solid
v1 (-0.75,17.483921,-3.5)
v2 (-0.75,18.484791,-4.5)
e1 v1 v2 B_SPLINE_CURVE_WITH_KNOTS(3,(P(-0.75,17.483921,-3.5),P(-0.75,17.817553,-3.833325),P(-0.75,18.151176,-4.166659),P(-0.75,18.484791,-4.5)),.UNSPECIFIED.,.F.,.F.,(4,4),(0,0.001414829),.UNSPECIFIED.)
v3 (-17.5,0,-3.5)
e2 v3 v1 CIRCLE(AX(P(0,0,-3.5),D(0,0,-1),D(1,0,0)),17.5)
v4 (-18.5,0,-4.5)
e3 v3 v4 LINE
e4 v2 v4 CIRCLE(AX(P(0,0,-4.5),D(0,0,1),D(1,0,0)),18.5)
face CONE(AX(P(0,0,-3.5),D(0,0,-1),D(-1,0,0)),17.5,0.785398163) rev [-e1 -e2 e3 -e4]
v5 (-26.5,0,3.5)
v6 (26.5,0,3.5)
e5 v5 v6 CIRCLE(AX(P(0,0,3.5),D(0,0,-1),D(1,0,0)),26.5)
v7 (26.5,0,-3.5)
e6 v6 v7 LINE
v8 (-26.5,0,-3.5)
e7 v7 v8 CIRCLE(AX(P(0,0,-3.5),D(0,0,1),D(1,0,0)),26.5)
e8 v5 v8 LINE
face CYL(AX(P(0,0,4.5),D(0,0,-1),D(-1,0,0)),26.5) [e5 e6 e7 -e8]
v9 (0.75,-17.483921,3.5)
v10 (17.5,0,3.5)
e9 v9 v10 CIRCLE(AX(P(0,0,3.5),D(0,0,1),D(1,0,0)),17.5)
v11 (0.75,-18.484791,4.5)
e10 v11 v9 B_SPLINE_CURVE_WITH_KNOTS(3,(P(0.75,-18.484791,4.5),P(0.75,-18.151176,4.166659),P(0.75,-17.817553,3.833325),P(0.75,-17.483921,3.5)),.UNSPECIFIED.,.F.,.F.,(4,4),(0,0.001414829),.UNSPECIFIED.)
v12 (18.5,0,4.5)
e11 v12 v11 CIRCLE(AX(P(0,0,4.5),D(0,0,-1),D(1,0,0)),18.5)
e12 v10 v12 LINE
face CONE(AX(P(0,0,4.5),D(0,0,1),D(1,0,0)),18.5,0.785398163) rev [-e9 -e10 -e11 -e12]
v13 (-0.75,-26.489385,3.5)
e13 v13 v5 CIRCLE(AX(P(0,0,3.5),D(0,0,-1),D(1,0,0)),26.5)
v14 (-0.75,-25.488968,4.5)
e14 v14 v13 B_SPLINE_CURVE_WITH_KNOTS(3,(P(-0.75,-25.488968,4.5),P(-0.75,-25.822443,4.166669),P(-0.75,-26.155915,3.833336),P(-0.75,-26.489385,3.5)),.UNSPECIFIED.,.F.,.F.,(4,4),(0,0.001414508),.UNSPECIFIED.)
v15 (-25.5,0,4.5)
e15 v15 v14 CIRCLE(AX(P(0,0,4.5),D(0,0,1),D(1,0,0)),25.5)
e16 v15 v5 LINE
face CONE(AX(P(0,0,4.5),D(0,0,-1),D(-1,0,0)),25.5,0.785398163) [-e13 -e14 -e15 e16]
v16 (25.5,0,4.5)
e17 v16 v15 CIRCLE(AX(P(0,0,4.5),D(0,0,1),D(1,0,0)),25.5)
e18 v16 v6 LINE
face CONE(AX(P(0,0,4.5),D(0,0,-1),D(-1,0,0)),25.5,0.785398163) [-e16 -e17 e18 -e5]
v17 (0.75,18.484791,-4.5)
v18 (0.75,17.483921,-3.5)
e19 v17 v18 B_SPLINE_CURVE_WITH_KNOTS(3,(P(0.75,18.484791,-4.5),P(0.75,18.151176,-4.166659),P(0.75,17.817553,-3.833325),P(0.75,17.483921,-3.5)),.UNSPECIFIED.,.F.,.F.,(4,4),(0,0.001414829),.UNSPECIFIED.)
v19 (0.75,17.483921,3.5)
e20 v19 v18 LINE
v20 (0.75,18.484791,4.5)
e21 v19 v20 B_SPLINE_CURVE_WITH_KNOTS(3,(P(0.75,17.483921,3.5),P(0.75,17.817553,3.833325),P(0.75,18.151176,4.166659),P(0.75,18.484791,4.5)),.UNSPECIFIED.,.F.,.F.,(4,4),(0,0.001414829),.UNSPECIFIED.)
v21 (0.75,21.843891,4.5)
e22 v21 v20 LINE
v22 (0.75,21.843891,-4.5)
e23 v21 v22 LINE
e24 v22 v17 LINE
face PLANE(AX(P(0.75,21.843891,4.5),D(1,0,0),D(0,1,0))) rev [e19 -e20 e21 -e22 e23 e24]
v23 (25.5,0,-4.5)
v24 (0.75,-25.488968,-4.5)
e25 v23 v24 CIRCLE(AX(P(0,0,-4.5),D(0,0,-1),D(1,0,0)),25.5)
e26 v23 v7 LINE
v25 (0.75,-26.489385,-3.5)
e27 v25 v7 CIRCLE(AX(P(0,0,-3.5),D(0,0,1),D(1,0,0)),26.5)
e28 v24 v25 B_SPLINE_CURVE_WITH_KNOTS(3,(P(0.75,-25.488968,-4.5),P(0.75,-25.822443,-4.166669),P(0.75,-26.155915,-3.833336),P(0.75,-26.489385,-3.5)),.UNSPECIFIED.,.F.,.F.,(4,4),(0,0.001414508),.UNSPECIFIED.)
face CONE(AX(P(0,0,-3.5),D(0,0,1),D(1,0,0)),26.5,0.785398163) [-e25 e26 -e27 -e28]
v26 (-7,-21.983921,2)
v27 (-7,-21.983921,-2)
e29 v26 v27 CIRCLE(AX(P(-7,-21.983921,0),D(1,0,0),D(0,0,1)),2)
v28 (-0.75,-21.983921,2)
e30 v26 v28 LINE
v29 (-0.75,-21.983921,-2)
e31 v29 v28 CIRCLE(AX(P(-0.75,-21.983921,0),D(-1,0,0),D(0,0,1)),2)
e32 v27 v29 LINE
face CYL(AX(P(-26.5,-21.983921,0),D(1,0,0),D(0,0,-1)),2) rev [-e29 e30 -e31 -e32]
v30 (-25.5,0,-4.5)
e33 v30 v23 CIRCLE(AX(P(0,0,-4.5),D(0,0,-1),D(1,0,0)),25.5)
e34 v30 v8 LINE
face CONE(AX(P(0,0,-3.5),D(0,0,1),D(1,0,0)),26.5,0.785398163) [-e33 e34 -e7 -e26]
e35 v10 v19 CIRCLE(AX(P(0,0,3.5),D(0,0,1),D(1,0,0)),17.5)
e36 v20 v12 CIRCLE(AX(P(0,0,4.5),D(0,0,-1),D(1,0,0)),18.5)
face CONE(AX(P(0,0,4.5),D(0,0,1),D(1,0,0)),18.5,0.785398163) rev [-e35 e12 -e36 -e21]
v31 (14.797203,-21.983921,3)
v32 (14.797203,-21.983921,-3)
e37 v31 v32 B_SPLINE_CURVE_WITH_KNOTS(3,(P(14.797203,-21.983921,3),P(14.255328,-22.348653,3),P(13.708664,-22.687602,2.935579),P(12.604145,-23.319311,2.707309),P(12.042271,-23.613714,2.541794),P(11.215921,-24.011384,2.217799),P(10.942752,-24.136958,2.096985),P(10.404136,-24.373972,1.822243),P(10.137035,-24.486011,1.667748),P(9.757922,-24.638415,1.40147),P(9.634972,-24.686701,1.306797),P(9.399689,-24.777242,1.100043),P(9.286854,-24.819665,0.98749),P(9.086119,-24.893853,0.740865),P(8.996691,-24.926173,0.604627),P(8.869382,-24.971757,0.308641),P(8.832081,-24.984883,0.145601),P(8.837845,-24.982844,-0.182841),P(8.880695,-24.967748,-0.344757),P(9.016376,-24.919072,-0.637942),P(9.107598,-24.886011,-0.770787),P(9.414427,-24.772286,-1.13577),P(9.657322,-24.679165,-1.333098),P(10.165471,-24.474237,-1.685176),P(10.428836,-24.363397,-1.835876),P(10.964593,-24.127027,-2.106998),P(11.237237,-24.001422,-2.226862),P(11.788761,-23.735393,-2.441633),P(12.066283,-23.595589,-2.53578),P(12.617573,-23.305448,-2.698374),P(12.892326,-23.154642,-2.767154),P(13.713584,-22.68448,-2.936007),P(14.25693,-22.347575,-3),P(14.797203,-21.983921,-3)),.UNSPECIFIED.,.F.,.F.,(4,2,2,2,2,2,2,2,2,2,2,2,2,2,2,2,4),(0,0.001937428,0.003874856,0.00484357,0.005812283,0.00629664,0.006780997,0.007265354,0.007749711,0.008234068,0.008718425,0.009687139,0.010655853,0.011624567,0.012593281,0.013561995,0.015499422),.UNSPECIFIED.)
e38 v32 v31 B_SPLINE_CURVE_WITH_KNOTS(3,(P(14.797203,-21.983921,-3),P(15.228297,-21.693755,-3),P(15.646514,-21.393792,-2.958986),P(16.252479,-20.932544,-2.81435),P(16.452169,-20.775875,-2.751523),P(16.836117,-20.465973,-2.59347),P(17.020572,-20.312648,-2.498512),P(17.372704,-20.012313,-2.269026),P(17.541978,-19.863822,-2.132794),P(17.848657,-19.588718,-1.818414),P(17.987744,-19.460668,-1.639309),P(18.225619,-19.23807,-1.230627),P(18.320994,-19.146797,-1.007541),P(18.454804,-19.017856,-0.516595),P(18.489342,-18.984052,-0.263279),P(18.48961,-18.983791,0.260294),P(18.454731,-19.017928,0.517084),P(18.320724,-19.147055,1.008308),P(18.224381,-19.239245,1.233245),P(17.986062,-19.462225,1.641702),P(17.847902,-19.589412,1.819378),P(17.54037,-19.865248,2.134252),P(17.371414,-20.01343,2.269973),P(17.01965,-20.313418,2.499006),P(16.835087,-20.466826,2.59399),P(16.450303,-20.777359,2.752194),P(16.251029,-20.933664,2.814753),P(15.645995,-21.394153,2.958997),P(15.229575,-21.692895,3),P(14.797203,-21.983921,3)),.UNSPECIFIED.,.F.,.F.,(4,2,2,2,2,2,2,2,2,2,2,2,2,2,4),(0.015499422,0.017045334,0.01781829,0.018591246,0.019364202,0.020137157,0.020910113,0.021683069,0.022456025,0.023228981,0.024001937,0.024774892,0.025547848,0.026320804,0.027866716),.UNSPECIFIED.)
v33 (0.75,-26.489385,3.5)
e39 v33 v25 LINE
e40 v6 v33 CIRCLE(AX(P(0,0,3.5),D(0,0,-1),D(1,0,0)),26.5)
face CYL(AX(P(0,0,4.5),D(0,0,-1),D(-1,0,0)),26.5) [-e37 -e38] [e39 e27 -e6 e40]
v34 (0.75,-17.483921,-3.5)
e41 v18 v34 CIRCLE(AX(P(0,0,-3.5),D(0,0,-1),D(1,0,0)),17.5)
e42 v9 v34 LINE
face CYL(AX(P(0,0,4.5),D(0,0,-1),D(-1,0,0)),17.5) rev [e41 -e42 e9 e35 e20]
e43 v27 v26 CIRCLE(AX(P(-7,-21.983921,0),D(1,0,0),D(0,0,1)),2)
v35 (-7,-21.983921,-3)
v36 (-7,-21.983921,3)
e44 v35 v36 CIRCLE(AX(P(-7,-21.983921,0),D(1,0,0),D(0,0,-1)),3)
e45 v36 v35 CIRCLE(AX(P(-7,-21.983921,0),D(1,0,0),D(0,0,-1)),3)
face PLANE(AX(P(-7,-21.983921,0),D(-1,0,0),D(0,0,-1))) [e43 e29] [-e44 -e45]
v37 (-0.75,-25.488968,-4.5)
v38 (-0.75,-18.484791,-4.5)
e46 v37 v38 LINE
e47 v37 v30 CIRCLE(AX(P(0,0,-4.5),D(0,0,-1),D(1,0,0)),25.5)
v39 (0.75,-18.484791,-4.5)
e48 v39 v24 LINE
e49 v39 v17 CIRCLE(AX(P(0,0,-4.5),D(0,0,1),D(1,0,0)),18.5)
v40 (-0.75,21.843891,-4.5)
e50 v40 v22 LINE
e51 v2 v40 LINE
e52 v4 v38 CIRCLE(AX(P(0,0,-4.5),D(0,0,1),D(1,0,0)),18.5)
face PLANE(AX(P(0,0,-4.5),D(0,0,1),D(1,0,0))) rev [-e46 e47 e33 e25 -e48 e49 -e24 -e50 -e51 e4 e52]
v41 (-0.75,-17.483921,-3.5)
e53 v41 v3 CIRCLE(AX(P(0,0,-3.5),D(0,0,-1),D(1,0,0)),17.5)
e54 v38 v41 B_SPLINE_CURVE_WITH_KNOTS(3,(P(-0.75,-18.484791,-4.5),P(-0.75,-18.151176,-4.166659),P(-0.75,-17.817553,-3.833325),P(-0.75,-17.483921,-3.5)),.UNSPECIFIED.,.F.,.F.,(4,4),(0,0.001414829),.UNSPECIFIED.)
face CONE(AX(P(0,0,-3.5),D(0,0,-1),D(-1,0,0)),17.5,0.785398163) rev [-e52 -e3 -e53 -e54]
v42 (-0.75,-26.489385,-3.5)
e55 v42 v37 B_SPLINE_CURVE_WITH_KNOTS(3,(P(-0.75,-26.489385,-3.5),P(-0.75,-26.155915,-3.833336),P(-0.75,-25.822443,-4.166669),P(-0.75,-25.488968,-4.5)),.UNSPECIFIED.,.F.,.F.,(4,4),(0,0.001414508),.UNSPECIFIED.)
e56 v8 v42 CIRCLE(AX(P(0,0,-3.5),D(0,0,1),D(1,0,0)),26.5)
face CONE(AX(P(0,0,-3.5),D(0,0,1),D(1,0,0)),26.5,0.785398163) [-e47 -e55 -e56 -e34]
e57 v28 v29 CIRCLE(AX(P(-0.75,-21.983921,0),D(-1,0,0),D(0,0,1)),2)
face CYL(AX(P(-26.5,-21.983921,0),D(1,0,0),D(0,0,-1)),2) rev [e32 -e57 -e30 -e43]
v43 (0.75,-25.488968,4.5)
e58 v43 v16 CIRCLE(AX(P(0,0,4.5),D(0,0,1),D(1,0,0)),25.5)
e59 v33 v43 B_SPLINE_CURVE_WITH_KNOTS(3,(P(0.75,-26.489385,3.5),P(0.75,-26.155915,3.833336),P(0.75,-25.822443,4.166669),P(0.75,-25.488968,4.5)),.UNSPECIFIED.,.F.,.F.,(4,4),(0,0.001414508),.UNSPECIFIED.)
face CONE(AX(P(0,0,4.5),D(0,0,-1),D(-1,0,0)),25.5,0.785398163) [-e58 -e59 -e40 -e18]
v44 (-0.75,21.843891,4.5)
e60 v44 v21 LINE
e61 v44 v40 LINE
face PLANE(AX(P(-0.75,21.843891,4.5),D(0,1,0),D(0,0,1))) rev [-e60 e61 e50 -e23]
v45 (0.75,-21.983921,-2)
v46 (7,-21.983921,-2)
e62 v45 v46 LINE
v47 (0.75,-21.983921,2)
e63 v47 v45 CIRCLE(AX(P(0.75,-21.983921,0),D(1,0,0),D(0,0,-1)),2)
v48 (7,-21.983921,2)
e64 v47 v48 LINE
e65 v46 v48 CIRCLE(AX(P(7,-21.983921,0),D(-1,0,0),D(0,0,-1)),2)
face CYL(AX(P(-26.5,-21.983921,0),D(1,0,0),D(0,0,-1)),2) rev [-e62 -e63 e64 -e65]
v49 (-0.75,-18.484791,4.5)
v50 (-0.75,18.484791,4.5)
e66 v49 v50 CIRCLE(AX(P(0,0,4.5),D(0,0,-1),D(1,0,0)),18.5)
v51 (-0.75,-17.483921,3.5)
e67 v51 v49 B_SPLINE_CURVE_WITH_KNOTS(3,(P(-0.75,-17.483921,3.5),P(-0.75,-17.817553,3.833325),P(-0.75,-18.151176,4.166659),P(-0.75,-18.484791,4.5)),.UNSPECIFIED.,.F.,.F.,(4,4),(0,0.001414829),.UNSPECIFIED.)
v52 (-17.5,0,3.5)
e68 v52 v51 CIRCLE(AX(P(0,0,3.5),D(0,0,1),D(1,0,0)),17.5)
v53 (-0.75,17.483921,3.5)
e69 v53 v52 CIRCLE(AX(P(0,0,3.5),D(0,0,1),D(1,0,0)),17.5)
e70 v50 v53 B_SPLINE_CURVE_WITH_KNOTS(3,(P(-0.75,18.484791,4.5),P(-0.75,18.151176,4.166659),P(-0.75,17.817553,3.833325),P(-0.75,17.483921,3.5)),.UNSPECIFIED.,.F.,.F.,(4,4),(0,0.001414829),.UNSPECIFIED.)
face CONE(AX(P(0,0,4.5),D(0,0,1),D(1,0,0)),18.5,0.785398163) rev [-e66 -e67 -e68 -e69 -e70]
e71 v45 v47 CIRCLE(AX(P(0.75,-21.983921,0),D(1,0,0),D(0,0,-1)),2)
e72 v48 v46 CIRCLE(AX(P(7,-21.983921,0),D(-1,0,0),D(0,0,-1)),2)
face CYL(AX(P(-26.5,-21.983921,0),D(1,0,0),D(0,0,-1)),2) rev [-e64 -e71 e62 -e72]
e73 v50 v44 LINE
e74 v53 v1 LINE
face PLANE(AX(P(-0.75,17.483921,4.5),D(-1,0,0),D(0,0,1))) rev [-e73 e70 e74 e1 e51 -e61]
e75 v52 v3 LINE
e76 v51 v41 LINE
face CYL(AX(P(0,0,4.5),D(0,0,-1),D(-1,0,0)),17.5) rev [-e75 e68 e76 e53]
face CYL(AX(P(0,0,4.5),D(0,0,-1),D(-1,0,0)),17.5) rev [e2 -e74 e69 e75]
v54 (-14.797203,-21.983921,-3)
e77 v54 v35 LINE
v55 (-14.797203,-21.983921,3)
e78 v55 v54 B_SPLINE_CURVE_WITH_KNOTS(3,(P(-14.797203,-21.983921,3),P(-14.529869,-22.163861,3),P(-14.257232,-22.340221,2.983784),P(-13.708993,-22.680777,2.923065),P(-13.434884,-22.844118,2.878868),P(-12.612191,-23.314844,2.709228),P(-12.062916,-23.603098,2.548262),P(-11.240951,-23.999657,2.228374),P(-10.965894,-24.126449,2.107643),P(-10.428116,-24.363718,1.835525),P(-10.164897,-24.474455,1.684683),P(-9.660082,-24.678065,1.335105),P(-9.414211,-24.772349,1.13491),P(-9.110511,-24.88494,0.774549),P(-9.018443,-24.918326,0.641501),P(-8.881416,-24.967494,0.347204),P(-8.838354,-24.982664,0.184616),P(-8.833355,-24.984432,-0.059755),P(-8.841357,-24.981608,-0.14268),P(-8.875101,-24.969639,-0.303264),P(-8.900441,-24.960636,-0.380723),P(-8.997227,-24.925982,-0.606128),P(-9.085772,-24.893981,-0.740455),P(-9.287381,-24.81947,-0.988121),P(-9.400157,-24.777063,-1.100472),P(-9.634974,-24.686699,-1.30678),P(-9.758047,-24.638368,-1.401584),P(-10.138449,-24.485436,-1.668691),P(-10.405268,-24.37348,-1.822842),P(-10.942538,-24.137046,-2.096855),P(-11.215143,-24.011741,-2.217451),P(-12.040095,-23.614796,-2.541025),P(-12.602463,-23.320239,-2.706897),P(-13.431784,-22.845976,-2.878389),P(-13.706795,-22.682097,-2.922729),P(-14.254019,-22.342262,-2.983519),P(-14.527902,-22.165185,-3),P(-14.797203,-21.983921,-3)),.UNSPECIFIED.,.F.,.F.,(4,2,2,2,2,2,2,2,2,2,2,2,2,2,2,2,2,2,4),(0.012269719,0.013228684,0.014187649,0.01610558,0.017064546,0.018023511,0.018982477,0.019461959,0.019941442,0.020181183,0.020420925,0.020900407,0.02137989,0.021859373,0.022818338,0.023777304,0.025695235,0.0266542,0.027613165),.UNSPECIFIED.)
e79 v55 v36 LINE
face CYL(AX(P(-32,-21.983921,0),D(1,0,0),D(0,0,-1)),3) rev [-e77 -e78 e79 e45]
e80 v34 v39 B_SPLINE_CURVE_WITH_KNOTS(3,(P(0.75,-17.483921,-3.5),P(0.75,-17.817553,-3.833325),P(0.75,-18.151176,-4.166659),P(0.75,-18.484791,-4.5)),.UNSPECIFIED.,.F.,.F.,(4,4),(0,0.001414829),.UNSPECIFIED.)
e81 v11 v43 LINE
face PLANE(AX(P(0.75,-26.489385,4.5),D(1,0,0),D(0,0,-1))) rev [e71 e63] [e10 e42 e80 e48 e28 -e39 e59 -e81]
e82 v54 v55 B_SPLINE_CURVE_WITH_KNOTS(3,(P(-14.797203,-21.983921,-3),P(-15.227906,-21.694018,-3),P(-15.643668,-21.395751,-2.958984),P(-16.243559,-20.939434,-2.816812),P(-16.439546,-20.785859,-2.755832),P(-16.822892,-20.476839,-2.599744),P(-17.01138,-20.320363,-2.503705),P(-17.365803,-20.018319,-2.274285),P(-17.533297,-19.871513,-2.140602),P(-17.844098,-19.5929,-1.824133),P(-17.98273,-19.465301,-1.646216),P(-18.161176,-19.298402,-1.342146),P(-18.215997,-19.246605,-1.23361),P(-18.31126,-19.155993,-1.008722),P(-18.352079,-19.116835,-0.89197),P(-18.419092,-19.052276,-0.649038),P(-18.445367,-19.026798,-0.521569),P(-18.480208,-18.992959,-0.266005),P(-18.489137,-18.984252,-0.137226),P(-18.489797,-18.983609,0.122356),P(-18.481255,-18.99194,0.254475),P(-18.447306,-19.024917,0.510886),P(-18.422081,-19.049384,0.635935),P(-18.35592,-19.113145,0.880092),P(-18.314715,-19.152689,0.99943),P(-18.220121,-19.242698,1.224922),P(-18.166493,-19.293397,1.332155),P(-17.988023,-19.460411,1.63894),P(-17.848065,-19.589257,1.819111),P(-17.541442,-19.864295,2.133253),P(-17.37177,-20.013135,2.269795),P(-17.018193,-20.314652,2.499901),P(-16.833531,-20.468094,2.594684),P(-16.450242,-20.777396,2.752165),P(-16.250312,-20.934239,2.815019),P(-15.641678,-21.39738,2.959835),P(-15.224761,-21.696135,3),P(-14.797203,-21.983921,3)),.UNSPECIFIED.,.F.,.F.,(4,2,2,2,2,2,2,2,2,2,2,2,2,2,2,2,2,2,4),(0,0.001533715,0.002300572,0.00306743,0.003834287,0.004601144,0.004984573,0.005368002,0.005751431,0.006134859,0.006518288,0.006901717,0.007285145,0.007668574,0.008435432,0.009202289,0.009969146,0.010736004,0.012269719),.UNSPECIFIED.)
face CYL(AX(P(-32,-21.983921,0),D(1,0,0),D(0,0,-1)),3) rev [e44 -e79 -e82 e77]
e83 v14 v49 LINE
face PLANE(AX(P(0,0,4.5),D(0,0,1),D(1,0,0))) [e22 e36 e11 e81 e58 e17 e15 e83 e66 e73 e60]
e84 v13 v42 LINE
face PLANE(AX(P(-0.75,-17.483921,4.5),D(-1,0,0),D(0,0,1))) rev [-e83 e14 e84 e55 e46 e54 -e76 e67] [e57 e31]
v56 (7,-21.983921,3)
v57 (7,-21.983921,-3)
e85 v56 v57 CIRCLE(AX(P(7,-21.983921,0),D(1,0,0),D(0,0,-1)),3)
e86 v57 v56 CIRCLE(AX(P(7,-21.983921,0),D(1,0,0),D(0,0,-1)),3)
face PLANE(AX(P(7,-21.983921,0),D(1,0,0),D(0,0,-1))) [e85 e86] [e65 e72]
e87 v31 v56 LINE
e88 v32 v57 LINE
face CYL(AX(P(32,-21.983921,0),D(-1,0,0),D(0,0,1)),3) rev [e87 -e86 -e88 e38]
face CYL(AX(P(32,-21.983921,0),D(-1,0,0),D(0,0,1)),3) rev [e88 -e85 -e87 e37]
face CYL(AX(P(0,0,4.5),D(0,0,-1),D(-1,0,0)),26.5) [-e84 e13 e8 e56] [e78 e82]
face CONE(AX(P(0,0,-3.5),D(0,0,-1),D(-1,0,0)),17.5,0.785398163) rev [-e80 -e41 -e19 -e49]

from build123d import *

# Parameters (mm, degrees)
RING_BODY_DEPTH       = 4.5
EDGE_CHAMFER_1MM_SIZE = 1
RADIAL_CUT_DEPTH      = 38.7458607
RADIAL_CUT_DEPTH_BACK = 38.7458607
RADIAL_CUT_SKETCH_R   = 2
SLOT_START            = 7
SLOT_SKETCH_R         = 3
SLOT_CUT_DEPTH        = 25


with BuildPart() as part:
    # Ring Profile Sketch → Ring Body (new, symmetric)
    with BuildSketch(Plane.XY):
        with BuildLine():
            Line((-0.75, 17.483921185), (-0.75, 21.843890817))
            Line((-0.75, 21.843890817), (0.75, 21.843890817))
            Line((0.75, 21.843890817), (0.75, 17.483921185))
            ThreePointArc((0.75, 17.483921185), (17.5, 0), (0.75, -17.483921185))
            Line((0.75, -17.483921185), (0.75, -26.489384666))
            ThreePointArc((0.75, -26.489384666), (0, 26.5), (-0.75, -26.489384666))
            Line((-0.75, -26.489384666), (-0.75, -17.483921185))
            ThreePointArc((-0.75, -17.483921185), (-17.5, 0), (-0.75, 17.483921185))
        make_face()
    extrude(amount=RING_BODY_DEPTH, both=True)

    # Edge Chamfer 1mm
    edge_chamfer_1mm_edges = [part.edges().sort_by_distance(p)[0] for p in [
        (-17.5, 0, -4.5),
        (17.5, 0, 4.5),
        (0, 26.5, 4.5),
        (-17.5, 0, 4.5),
        (0, 26.5, -4.5),
        (17.5, 0, -4.5),
    ]]
    chamfer(edge_chamfer_1mm_edges, length=EDGE_CHAMFER_1MM_SIZE)

    # Radial Cut Sketch → Radial Cut (cut, two sides: drawn at the far end of the back side and taken through both)
    with BuildSketch(Plane(origin=(0, 0, 0), x_dir=(0, 0, -1), z_dir=(1, 0, 0)).offset(-RADIAL_CUT_DEPTH_BACK)):
        with Locations((0, -21.983921185)):
            Circle(RADIAL_CUT_SKETCH_R)
    extrude(amount=RADIAL_CUT_DEPTH + RADIAL_CUT_DEPTH_BACK, mode=Mode.SUBTRACT)

    # Slot Sketch → Slot Cut (cut)
    with BuildSketch(Plane(origin=(0, 0, 0), x_dir=(0, 0, -1), z_dir=(1, 0, 0)).offset(SLOT_START)):
        with Locations(Location((0, -21.983921185, 0), (0, 0, 180))):
            Circle(SLOT_SKETCH_R)
    slot_cut = extrude(amount=SLOT_CUT_DEPTH, mode=Mode.SUBTRACT)

    # Slot Mirror: Slot Cut across plane
    add(slot_cut.mirror(Plane(origin=(0, 0, 0), x_dir=(0, 0, 1), z_dir=(1, 0, 0))), mode=Mode.SUBTRACT)


solid = part.part
